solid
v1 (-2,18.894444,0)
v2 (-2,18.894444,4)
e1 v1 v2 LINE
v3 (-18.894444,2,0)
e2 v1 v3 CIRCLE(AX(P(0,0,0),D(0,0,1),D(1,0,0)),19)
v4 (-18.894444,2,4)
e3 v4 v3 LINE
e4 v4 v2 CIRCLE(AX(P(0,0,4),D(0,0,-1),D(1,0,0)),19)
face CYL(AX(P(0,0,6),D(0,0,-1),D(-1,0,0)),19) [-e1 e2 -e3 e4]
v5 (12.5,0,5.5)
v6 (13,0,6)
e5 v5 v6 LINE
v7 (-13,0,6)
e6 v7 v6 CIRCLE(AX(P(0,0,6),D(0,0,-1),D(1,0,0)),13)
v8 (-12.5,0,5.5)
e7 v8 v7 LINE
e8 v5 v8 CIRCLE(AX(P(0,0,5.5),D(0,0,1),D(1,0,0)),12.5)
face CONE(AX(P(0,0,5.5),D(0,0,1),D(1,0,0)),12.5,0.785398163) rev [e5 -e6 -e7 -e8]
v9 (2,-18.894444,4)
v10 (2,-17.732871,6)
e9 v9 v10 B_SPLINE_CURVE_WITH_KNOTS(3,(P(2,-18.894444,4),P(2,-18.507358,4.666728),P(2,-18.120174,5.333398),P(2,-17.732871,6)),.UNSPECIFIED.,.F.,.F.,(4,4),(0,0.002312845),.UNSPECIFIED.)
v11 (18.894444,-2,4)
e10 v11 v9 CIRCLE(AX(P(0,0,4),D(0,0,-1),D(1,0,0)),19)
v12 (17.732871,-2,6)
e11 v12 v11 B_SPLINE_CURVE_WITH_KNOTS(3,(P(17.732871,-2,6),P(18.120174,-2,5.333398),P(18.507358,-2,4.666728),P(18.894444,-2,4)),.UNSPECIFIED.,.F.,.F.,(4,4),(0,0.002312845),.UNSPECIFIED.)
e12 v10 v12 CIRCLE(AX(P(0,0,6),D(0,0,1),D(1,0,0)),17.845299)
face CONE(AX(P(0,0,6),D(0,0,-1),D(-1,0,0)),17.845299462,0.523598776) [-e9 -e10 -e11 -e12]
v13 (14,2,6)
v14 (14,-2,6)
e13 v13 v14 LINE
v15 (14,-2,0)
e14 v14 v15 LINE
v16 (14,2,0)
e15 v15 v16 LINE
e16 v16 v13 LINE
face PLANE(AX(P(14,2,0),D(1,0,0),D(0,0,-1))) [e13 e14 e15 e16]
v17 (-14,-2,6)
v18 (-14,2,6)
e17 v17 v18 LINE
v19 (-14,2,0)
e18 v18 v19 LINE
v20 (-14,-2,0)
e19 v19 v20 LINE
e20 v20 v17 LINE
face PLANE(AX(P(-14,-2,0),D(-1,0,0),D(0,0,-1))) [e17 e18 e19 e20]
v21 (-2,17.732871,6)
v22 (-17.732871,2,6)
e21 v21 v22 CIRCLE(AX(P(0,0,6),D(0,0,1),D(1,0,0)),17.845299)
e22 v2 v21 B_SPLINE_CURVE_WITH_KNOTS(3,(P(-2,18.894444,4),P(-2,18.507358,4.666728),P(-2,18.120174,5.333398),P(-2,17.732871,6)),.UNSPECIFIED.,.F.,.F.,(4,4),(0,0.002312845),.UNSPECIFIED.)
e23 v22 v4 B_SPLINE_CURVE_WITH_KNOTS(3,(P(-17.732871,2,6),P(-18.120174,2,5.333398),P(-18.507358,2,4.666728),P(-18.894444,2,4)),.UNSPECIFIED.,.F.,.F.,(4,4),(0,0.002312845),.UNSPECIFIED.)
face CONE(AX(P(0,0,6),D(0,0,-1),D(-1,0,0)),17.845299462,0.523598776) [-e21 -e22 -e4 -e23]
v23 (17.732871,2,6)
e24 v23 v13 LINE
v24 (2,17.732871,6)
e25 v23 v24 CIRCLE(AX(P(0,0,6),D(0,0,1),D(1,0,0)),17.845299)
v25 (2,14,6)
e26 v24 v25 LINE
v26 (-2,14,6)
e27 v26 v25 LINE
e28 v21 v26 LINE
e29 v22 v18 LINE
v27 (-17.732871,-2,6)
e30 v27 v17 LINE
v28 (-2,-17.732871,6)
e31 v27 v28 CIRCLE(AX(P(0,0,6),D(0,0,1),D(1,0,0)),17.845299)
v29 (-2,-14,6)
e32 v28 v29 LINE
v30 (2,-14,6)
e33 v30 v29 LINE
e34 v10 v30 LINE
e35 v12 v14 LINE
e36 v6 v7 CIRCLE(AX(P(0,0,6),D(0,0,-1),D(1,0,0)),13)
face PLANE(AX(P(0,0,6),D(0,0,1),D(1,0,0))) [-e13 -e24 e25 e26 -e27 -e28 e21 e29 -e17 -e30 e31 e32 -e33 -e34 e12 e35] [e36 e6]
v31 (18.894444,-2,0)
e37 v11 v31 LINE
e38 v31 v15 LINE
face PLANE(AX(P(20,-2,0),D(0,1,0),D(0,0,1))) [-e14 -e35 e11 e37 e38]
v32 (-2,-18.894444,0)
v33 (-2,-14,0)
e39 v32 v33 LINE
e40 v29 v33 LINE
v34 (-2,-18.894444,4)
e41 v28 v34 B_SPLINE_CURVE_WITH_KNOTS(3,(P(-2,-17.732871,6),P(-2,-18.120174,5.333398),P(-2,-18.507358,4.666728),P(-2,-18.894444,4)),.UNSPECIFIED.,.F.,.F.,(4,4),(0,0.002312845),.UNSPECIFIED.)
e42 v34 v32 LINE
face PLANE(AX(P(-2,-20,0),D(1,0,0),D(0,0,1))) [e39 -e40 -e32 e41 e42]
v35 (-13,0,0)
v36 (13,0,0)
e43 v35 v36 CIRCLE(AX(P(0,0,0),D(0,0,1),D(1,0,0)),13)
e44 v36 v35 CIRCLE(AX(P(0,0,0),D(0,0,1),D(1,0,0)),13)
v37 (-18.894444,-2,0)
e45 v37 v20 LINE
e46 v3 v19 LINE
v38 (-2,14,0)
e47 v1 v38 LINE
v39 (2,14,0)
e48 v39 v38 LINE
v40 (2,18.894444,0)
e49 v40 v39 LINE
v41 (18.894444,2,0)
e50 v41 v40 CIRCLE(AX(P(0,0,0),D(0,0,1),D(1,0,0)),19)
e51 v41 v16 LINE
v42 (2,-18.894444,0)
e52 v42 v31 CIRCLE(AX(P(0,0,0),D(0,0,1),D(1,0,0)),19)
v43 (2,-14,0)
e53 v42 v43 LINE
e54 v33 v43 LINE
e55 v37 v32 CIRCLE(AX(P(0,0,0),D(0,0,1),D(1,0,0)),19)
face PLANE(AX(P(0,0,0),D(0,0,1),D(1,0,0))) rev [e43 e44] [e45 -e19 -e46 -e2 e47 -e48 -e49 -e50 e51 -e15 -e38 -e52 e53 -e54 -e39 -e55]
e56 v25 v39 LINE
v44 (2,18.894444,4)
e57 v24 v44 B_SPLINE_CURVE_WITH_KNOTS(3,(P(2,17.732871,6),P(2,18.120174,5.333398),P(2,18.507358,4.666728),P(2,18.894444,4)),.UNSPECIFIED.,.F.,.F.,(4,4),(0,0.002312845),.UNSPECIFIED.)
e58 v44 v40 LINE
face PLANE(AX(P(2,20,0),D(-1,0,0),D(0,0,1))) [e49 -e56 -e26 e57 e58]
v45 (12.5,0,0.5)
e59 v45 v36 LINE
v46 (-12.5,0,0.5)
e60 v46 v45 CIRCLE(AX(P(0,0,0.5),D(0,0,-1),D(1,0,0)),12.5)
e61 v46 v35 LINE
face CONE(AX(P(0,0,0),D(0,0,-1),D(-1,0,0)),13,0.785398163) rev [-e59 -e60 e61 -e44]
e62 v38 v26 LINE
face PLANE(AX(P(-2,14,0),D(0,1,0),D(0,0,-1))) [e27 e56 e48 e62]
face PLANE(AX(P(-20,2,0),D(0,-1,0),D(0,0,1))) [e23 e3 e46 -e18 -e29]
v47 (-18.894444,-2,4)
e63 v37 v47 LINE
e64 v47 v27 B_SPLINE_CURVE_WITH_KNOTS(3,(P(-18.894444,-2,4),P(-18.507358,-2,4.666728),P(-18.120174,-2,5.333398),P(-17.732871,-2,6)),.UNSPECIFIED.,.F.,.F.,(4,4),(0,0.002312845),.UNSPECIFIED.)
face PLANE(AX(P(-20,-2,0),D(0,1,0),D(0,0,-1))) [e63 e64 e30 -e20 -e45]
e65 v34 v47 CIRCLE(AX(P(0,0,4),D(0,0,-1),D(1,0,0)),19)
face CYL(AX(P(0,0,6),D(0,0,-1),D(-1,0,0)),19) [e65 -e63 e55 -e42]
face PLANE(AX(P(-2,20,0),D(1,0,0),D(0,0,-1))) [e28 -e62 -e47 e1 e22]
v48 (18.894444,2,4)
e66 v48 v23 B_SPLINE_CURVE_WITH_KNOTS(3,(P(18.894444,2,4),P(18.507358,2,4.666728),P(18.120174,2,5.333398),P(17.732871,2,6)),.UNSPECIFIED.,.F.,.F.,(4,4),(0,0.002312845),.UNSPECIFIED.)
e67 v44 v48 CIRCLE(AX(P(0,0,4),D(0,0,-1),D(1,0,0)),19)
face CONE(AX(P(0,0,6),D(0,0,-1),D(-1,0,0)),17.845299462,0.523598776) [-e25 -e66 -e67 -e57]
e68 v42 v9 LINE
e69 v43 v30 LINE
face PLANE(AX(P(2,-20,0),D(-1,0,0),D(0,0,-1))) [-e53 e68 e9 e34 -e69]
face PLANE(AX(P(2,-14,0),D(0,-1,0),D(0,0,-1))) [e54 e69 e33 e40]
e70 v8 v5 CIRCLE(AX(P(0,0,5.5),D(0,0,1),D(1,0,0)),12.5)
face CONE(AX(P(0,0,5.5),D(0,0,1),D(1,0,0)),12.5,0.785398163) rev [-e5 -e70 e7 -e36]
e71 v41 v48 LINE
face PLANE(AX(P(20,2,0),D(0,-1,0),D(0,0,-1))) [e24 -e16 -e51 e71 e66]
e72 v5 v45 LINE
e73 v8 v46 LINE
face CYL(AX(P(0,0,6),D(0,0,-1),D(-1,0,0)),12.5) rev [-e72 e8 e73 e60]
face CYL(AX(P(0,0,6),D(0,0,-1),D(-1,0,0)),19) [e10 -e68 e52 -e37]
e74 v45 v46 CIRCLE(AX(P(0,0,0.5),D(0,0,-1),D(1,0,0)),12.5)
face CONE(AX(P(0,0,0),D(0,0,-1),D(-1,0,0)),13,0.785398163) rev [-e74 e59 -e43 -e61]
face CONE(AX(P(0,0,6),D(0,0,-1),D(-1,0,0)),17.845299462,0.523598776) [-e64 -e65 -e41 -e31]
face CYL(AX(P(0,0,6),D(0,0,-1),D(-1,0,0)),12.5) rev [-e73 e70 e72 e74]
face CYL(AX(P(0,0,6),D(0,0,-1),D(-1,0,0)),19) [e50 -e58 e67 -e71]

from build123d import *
from OCP.BRepFilletAPI import BRepFilletAPI_MakeChamfer

# Parameters (mm, degrees)
SKETCH1_R           = 19
SKETCH1_R_2         = 12.5
BOSS_EXTRUDE1_DEPTH = 6
SKETCH2_W           = 6
SKETCH2_H           = 4
CUT_EXTRUDE1_DEPTH  = 6
CIRPATTERN1_COUNT   = 4
CHAMFER1_SIZE       = 0.5
CHAMFER2_SIZE       = 2
CHAMFER2_SIZE2      = 1.154700538


with BuildPart() as part:
    # Sketch1 → Boss-Extrude1 (new body)
    with BuildSketch(Plane.XY):
        Circle(SKETCH1_R)
        Circle(SKETCH1_R_2, mode=Mode.SUBTRACT)
    extrude(amount=BOSS_EXTRUDE1_DEPTH)

    # Sketch2 → Cut-Extrude1 (cut)
    with BuildSketch(Plane(origin=(14, 0, 0), x_dir=(0, 0, -1), z_dir=(1, 0, 0))):
        with Locations((-3, 0)):
            Rectangle(SKETCH2_W, SKETCH2_H)
    cut_extrude1 = extrude(amount=CUT_EXTRUDE1_DEPTH, mode=Mode.SUBTRACT)

    # CirPattern1: Cut-Extrude1 ×4 about axis
    cirpattern1_axis = Axis((0, 0, 0), (0, 0, 1))
    for i in range(1, CIRPATTERN1_COUNT):
        add(cut_extrude1.rotate(cirpattern1_axis, i * 360 / CIRPATTERN1_COUNT), mode=Mode.SUBTRACT)

    # Chamfer1
    chamfer1_edges = [part.edges().sort_by_distance(p)[0] for p in [
        (-12.5, 0, 0),
        (-12.5, 0, 6),
    ]]
    chamfer(chamfer1_edges, length=CHAMFER1_SIZE)

    # Chamfer2: one chamfer whose edges measure the first distance from different faces: ONE call of the kernel's chamfer builder (chamfer() names one face for all edges)
    chamfer2_edges_1 = [part.edges().sort_by_distance(p)[0] for p in [
        (13.435028843, -13.435028843, 6),
    ]]
    chamfer2_side_1 = [part.faces().sort_by_distance(p)[0] for p in [
        (13.435028843, -13.435028843, 3),
    ]]
    chamfer2_edges_2 = [part.edges().sort_by_distance(p)[0] for p in [
        (13.435028843, 13.435028843, 6),
    ]]
    chamfer2_side_2 = [part.faces().sort_by_distance(p)[0] for p in [
        (13.435028843, 13.435028843, 3),
    ]]
    chamfer2_edges_3 = [part.edges().sort_by_distance(p)[0] for p in [
        (-13.435028843, -13.435028843, 6),
    ]]
    chamfer2_side_3 = [part.faces().sort_by_distance(p)[0] for p in [
        (-13.435028843, -13.435028843, 3),
    ]]
    chamfer2_edges_4 = [part.edges().sort_by_distance(p)[0] for p in [
        (-13.435028843, 13.435028843, 6),
    ]]
    chamfer2_side_4 = [part.faces().sort_by_distance(p)[0] for p in [
        (-13.435028843, 13.435028843, 3),
    ]]
    chamfer2 = BRepFilletAPI_MakeChamfer(part.part.solid().wrapped)
    for e in chamfer2_edges_1:
        chamfer2.Add(CHAMFER2_SIZE, CHAMFER2_SIZE2, e.wrapped, chamfer2_side_1[0].wrapped)  # the first distance lies on this face
    for e in chamfer2_edges_2:
        chamfer2.Add(CHAMFER2_SIZE, CHAMFER2_SIZE2, e.wrapped, chamfer2_side_2[0].wrapped)  # the first distance lies on this face
    for e in chamfer2_edges_3:
        chamfer2.Add(CHAMFER2_SIZE, CHAMFER2_SIZE2, e.wrapped, chamfer2_side_3[0].wrapped)  # the first distance lies on this face
    for e in chamfer2_edges_4:
        chamfer2.Add(CHAMFER2_SIZE, CHAMFER2_SIZE2, e.wrapped, chamfer2_side_4[0].wrapped)  # the first distance lies on this face
    add(Compound.cast(chamfer2.Shape()), mode=Mode.REPLACE)


solid = part.part
